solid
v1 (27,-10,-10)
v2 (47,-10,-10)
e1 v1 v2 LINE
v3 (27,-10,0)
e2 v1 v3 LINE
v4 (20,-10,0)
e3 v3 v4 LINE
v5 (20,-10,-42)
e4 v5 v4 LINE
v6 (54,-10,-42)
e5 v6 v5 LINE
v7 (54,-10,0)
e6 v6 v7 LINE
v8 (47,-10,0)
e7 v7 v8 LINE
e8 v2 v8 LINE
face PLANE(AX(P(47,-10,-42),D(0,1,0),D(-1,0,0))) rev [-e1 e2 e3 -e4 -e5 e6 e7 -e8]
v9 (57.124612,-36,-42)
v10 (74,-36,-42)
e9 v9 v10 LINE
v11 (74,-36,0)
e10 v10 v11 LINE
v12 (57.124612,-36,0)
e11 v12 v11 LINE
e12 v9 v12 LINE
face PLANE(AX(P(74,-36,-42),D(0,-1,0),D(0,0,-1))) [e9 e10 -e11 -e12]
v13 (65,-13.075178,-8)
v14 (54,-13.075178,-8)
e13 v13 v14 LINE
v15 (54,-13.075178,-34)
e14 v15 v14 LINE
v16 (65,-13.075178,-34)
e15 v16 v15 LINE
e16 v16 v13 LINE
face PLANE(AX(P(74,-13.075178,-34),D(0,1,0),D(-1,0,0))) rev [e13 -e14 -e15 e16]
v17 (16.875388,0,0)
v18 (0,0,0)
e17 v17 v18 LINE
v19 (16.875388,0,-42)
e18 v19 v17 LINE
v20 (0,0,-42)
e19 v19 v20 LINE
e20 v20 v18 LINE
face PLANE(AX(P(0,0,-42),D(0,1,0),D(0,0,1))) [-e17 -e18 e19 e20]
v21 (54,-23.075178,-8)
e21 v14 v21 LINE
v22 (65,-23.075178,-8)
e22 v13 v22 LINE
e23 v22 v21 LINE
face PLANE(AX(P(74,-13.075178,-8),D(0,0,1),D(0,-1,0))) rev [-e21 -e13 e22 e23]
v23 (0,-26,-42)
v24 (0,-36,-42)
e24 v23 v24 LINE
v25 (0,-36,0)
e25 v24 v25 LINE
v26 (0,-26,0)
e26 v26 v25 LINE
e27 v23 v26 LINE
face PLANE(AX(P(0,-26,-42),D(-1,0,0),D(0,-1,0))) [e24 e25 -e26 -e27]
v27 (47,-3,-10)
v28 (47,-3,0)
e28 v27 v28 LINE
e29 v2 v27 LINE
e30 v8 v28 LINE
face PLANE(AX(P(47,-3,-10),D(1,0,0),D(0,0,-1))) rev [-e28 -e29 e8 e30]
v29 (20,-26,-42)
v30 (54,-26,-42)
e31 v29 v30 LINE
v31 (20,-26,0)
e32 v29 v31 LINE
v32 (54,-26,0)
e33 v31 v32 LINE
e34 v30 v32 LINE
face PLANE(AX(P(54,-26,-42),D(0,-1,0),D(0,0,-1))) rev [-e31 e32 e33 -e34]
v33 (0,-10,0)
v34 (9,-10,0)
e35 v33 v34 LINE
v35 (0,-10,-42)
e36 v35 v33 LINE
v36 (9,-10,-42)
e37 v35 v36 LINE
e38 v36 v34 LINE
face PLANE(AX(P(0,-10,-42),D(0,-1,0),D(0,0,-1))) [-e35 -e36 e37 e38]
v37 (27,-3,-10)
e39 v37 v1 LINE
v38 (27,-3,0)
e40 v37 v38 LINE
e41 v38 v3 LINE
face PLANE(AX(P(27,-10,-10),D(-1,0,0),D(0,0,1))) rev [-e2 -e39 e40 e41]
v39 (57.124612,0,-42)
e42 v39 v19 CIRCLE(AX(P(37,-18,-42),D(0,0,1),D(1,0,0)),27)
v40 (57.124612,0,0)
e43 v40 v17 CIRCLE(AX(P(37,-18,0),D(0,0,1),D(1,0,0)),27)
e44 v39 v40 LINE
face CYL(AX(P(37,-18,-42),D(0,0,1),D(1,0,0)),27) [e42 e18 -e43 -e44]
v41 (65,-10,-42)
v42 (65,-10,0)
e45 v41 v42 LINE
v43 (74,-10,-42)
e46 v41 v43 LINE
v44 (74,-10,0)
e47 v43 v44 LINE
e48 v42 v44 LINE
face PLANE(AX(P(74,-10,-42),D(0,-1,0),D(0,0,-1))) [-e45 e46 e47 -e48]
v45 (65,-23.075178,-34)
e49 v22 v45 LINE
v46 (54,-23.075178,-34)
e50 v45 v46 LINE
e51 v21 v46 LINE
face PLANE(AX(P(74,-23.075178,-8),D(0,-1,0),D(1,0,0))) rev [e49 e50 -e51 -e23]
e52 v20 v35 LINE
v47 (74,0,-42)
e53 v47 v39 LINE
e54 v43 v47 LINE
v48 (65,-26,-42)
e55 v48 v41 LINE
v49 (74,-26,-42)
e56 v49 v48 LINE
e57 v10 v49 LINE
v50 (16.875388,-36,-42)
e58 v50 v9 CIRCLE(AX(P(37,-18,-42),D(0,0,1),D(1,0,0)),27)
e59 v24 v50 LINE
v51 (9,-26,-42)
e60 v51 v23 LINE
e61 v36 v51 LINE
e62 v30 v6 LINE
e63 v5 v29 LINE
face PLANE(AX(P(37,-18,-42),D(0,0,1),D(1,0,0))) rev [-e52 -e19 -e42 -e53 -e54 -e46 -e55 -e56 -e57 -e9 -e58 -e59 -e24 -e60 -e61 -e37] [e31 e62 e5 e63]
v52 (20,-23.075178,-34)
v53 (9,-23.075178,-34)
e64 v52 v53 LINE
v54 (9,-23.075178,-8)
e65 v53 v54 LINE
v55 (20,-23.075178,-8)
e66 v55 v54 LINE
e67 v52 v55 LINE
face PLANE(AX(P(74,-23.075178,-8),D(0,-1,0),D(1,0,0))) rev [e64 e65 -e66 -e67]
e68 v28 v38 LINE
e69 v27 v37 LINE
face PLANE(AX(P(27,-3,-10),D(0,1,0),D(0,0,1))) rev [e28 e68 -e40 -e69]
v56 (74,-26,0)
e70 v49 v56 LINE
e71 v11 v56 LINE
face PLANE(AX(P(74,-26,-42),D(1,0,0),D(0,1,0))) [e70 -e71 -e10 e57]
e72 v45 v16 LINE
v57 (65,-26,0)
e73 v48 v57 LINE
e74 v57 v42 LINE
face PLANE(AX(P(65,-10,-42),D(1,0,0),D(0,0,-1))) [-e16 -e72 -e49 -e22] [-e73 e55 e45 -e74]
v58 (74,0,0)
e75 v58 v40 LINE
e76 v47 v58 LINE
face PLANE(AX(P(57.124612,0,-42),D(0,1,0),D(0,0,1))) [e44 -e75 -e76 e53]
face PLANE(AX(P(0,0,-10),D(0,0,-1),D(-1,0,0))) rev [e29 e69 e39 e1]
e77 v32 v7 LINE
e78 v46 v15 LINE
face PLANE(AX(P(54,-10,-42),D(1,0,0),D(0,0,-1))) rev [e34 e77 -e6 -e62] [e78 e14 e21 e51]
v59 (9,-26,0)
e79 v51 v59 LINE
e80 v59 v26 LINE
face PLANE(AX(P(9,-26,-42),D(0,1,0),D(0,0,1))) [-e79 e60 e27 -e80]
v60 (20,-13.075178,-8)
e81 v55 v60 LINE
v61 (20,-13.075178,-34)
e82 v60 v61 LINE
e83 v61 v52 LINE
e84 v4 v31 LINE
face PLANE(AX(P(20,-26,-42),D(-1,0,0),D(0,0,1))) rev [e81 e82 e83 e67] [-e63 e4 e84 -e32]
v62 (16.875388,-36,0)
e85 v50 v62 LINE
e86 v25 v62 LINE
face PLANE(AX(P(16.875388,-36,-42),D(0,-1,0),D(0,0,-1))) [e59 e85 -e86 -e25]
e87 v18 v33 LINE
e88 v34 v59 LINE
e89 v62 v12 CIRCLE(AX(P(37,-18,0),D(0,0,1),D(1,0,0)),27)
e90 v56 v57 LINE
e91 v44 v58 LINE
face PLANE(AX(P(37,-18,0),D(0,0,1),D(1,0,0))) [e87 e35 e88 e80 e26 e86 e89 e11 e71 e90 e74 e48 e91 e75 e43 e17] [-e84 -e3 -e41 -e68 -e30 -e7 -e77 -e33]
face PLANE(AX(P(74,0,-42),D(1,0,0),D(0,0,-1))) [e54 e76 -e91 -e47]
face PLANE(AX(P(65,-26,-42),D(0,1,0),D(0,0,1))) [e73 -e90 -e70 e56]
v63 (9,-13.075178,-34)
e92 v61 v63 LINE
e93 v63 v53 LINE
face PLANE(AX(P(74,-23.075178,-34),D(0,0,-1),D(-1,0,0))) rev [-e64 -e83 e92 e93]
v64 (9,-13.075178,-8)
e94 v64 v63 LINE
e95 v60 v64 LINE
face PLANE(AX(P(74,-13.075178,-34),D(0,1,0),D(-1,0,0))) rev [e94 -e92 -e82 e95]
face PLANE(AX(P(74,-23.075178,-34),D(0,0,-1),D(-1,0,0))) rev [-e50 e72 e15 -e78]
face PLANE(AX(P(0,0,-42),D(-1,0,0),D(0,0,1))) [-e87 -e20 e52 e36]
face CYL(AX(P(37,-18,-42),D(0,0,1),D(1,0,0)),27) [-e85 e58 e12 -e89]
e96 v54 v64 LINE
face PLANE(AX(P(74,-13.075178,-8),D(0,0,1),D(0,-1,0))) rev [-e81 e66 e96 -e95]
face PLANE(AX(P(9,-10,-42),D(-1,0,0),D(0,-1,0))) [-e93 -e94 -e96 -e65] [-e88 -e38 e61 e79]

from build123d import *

# Parameters (mm, degrees)
BLOCK_EXTRUDE_42_DEPTH     = 42
THROUGH_WINDOW_CUT_DEPTH   = 97.254870007
POCKET_20X7_SKETCH_W       = 20
POCKET_20X7_SKETCH_H       = 7
POCKET_20X7_DEPTH_10_DEPTH = 10
SIDE_SLOT_SKETCH_W         = 26
SIDE_SLOT_SKETCH_H         = 10
SIDE_SLOT_CUT_26X8_DEPTH   = 90.520947269


with BuildPart() as part:
    # Block Profile Sketch → Block Extrude 42 (new body)
    with BuildSketch(Plane.XY):
        with BuildLine():
            Line((0, 0), (16.875388203, 0))
            ThreePointArc((16.875388203, 0), (37, 9), (57.124611797, 0))
            Line((57.124611797, 0), (74, 0))
            Line((74, 0), (74, -10))
            Line((74, -10), (65, -10))
            Line((65, -10), (65, -26))
            Line((65, -26), (74, -26))
            Line((74, -26), (74, -36))
            Line((74, -36), (57.124611797, -36))
            ThreePointArc((57.124611797, -36), (37, -45), (16.875388203, -36))
            Line((16.875388203, -36), (0, -36))
            Line((0, -36), (0, -26))
            Line((0, -26), (9, -26))
            Line((9, -26), (9, -10))
            Line((9, -10), (0, -10))
            Line((0, -10), (0, 0))
        make_face()
    extrude(amount=-BLOCK_EXTRUDE_42_DEPTH)

    # Through Window Sketch → Through Window Cut (cut, through all)
    with BuildSketch(Plane.XY):
        Polygon((47, -10), (54, -10), (54, -26), (20, -26), (20, -10), (27, -10), align=None)
    extrude(amount=-THROUGH_WINDOW_CUT_DEPTH, mode=Mode.SUBTRACT)

    # Pocket 20x7 Sketch → Pocket 20x7 Depth 10 (cut)
    with BuildSketch(Plane.XY):
        with Locations((37, -6.5)):
            Rectangle(POCKET_20X7_SKETCH_W, POCKET_20X7_SKETCH_H)
    extrude(amount=-POCKET_20X7_DEPTH_10_DEPTH, mode=Mode.SUBTRACT)

    # Side Slot Sketch → Side Slot Cut 26x8 (cut, through all)
    with BuildSketch(Plane.ZY.offset(-9)):
        with Locations((-21, -18.075177639)):
            Rectangle(SIDE_SLOT_SKETCH_W, SIDE_SLOT_SKETCH_H)
    extrude(amount=-SIDE_SLOT_CUT_26X8_DEPTH, mode=Mode.SUBTRACT)


solid = part.part
